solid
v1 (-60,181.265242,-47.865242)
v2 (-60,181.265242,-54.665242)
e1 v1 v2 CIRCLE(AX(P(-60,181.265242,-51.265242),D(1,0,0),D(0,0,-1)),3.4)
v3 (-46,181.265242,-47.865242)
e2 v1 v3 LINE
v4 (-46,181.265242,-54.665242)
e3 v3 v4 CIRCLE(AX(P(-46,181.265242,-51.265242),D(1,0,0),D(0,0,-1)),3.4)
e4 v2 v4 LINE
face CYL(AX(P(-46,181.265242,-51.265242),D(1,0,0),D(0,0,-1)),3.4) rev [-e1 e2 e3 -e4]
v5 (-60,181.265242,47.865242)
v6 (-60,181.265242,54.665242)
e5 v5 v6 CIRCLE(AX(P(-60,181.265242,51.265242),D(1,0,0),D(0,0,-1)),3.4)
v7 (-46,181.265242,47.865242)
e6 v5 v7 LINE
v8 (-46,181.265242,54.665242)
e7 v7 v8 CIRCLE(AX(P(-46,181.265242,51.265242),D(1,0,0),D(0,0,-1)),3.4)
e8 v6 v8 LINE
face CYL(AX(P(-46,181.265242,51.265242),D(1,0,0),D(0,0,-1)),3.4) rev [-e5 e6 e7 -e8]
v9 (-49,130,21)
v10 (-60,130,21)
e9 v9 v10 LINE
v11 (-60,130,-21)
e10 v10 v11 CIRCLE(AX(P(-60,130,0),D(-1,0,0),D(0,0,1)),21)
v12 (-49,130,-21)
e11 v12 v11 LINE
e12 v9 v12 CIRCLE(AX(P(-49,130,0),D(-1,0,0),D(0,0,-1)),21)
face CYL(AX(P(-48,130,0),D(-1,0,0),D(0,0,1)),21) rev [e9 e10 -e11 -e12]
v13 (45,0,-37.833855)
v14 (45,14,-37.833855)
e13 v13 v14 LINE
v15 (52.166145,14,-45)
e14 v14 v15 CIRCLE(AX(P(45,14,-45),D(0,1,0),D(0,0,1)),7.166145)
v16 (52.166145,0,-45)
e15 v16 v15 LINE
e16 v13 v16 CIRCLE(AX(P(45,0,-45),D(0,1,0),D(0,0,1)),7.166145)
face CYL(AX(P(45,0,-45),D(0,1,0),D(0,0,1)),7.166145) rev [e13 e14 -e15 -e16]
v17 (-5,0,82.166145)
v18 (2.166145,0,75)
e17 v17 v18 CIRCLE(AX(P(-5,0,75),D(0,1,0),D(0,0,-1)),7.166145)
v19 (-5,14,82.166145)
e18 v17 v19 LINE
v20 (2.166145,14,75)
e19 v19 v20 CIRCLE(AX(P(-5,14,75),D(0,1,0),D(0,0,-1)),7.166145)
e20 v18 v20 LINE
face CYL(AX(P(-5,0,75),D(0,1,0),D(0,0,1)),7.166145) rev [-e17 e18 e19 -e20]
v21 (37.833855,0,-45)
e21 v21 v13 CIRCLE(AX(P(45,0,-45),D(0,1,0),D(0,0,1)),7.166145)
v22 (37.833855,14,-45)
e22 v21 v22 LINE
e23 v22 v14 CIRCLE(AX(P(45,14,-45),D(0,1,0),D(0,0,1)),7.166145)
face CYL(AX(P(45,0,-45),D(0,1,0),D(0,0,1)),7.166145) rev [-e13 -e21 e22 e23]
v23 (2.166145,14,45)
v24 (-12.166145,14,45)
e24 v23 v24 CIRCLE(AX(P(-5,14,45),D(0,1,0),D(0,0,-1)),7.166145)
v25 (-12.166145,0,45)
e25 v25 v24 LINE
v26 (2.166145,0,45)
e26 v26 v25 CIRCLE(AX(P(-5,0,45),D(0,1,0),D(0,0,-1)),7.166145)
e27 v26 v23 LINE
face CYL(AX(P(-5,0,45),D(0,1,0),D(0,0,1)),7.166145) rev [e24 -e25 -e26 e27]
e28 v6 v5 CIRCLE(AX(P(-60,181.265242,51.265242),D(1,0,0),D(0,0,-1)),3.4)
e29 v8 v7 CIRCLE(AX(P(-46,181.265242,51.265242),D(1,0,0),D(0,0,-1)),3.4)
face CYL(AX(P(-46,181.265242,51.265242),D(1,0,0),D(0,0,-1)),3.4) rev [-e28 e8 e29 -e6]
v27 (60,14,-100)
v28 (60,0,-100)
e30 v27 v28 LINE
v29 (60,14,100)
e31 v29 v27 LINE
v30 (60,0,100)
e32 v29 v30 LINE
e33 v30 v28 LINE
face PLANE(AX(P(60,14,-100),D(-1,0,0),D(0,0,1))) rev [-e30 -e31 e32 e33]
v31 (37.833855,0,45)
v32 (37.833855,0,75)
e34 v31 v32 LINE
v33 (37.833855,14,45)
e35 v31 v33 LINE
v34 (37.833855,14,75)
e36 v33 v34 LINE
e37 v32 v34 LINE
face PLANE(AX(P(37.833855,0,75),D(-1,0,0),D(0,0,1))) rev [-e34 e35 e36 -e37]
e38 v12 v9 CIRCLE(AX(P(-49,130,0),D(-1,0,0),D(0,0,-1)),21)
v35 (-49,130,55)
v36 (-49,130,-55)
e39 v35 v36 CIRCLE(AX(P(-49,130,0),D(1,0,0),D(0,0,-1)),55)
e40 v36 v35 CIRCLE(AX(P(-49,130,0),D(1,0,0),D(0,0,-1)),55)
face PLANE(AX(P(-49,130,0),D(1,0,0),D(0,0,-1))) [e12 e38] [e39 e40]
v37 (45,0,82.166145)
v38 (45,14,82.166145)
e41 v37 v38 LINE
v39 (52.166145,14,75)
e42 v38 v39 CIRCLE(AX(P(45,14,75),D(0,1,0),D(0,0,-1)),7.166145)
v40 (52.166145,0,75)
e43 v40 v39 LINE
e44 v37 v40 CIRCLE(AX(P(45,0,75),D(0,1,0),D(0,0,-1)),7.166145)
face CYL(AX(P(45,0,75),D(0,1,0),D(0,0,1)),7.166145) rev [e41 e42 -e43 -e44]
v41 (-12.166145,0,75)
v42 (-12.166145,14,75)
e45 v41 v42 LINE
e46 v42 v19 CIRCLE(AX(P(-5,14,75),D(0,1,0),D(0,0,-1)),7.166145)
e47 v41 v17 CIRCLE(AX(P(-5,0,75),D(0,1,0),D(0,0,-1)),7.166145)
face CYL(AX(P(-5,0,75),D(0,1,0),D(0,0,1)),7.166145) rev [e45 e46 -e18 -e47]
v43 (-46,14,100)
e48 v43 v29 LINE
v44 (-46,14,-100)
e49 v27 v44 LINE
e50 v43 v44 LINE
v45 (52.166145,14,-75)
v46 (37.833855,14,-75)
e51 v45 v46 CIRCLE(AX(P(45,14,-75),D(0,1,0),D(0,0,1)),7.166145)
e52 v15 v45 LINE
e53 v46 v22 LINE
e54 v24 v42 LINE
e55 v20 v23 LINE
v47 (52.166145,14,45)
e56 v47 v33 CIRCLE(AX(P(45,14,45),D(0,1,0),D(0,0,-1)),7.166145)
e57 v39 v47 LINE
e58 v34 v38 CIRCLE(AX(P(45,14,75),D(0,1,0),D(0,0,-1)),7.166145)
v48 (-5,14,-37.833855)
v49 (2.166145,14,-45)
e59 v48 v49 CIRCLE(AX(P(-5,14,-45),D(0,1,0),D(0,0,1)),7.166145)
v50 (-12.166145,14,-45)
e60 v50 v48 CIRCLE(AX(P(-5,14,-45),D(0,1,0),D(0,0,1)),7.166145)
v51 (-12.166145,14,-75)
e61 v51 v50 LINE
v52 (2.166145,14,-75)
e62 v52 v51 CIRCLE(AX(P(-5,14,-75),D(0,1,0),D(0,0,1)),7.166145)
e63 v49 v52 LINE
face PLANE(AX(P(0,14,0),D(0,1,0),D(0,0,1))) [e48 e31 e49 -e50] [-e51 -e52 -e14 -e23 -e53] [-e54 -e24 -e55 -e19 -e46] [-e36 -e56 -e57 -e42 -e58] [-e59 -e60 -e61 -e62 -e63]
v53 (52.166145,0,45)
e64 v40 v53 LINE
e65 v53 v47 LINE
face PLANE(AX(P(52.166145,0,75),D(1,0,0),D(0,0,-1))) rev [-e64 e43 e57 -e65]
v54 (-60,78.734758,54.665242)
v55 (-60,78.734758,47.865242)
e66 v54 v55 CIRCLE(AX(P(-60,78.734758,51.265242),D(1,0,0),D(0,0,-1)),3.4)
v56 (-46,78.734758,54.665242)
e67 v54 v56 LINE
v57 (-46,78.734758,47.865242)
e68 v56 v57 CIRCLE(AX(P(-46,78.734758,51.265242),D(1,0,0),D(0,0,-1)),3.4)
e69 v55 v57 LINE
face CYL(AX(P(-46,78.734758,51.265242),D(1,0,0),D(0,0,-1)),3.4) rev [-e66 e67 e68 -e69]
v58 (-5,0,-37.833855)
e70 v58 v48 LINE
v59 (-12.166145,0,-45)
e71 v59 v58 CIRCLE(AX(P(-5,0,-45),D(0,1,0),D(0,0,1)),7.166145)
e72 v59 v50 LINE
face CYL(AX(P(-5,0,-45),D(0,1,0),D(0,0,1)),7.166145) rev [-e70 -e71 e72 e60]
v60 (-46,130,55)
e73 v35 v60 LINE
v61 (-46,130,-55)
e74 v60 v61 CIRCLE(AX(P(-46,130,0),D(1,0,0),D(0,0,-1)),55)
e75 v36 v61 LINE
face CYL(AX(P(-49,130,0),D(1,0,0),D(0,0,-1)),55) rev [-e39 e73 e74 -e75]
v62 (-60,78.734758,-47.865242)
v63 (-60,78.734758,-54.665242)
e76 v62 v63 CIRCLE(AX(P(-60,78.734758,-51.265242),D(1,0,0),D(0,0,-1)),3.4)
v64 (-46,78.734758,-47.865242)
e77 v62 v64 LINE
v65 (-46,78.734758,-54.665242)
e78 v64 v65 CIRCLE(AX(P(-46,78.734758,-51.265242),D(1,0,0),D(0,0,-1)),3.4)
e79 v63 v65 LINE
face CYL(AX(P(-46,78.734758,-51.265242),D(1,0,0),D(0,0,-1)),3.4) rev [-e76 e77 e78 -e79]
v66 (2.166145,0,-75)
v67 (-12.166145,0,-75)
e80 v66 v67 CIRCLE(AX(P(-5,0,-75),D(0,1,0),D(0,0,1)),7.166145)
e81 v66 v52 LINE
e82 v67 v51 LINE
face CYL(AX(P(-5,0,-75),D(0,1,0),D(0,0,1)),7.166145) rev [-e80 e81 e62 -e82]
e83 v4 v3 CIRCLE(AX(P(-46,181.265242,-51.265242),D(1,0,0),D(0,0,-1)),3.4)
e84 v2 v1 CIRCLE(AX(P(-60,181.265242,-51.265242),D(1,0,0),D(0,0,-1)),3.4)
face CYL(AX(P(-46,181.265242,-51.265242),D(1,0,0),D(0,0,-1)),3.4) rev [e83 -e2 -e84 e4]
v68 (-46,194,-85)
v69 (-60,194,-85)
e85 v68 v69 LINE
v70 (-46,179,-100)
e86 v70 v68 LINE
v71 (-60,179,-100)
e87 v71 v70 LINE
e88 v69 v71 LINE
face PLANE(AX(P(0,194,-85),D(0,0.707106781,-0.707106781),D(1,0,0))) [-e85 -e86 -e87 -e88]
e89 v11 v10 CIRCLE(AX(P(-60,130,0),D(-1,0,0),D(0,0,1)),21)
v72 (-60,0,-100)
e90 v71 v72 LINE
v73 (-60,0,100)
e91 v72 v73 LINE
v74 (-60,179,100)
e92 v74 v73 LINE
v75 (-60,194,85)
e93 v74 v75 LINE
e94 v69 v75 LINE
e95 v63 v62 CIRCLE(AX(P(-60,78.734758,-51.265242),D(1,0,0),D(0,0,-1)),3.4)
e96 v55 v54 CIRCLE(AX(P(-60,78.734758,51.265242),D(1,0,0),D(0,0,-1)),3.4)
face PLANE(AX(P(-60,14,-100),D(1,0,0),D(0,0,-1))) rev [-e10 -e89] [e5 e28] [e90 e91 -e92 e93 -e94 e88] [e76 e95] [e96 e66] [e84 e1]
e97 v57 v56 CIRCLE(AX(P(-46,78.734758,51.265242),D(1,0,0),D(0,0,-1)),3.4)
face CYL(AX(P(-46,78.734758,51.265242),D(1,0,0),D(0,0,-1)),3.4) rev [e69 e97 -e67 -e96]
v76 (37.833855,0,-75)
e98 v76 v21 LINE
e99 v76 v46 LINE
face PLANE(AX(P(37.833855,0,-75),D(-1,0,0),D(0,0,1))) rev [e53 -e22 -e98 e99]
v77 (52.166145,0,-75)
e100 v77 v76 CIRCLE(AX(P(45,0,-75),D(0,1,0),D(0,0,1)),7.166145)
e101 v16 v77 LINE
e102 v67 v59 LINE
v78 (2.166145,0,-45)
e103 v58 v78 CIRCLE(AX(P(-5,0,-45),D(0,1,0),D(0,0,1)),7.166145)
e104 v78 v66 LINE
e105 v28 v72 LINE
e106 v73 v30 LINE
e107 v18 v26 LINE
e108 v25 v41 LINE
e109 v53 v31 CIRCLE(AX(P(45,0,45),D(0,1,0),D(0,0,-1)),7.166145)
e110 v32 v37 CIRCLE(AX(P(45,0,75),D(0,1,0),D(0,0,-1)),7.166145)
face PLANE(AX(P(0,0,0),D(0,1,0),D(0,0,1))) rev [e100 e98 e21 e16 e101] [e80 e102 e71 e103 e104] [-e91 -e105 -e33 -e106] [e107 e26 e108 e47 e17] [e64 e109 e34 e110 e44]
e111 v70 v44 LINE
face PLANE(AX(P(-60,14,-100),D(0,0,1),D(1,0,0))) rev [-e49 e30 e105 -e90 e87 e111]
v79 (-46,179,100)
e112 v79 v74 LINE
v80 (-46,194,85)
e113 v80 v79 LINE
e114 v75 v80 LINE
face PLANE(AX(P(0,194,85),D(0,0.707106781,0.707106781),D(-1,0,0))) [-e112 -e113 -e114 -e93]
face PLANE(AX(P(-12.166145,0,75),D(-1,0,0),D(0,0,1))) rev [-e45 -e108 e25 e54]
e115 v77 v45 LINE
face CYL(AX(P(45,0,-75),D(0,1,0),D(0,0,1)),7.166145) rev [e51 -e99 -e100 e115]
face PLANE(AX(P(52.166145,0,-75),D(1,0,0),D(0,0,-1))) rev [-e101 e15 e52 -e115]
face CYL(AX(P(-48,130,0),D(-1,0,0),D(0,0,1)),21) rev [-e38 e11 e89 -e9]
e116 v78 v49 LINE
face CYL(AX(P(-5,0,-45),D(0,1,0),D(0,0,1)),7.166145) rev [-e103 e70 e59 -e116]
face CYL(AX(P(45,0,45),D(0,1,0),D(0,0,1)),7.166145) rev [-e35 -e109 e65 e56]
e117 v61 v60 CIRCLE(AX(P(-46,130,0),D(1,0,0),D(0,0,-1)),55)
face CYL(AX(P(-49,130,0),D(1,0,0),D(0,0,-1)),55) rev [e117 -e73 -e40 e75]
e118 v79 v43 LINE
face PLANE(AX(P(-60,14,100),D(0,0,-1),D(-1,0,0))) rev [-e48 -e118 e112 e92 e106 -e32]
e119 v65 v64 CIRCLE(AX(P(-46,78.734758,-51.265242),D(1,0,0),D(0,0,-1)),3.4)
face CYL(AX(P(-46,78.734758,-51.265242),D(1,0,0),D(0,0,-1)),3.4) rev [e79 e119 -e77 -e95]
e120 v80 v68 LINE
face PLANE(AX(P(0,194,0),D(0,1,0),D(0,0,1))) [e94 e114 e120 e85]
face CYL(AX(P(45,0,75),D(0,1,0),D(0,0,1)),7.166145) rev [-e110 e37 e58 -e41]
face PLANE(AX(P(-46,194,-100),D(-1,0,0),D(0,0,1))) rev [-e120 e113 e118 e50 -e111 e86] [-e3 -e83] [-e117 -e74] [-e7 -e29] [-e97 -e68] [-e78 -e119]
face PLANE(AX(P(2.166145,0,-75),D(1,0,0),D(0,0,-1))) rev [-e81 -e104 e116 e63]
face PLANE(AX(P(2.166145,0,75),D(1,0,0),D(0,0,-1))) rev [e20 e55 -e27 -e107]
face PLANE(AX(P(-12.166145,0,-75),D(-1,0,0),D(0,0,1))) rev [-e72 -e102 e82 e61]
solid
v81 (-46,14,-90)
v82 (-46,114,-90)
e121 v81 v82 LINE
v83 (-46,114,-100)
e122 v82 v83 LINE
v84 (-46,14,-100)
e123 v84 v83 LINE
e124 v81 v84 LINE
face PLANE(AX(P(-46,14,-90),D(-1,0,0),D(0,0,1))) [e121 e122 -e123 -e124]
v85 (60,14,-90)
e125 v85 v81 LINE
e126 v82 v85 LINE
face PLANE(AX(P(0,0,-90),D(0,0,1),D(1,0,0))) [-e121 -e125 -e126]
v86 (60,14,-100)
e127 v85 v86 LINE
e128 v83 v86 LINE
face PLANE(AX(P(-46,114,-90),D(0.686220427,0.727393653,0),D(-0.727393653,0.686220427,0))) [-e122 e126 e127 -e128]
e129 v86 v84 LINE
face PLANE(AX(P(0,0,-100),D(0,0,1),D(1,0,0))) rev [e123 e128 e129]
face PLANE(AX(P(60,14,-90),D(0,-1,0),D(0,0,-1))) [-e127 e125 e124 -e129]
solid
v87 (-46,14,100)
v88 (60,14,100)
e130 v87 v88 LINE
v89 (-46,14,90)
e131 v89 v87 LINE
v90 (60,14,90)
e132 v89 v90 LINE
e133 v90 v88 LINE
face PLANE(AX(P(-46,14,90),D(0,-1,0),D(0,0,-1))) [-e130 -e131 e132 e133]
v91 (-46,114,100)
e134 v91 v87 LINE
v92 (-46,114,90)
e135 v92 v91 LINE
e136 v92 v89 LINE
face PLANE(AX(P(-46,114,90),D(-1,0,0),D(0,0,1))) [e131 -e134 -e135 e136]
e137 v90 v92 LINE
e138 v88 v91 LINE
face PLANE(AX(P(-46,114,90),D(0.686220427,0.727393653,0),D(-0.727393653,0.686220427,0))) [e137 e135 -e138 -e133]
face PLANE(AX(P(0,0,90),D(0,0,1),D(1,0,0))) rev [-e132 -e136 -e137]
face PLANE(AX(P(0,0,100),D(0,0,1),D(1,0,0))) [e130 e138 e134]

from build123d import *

# Parameters (mm, degrees)
SKETCH_1_W               = 120
SKETCH_1_H               = 200
EXTRUDE_1_DEPTH          = 14
SKETCH_2_W               = 14
SKETCH_2_H               = 200
EXTRUDE_2_DEPTH          = 180
EXTRUDE_3_DEPTH          = 10
EXTRUDE_4_DEPTH          = 10
SKETCH_5_R               = 21
CUT_EXTRUDE_1_DEPTH      = 12
SKETCH_6_R               = 15
CUT_EXTRUDE_2_DEPTH      = 244.515913238
SKETCH_7_R               = 55
CUT_EXTRUDE_3_DEPTH      = 3
CUT_EXTRUDE_4_DEPTH      = 215.476105895
SKETCH_10_W              = 3.4
SKETCH_10_H              = 14
PATTERN_CIRCULAR_1_COUNT = 4
CHAMFER_1_SIZE           = 15


with BuildPart() as part:
    # 草图1 → 凸台-拉伸1 (new body)
    with BuildSketch(Plane(origin=(0, 0, 0), x_dir=(1, 0, 0), z_dir=(0, 1, 0))):
        Rectangle(SKETCH_1_W, SKETCH_1_H)
    extrude(amount=EXTRUDE_1_DEPTH)

    # 草图2 → 凸台-拉伸2 (add)
    with BuildSketch(Plane(origin=(0, 14, 0), x_dir=(1, 0, 0), z_dir=(0, 1, 0))):
        with Locations((-53, 0)):
            Rectangle(SKETCH_2_W, SKETCH_2_H)
    extrude(amount=EXTRUDE_2_DEPTH)

    # 草图5 → 切除-拉伸1 (cut)
    with BuildSketch(Plane.ZY.offset(60)):
        with Locations((0, 130)):
            Circle(SKETCH_5_R)
    extrude(amount=-CUT_EXTRUDE_1_DEPTH, mode=Mode.SUBTRACT)

    # 草图6 → 切除-拉伸2 (cut, through all)
    with BuildSketch(Plane.ZY.offset(48)):
        with Locations((0, 130)):
            Circle(SKETCH_6_R)
    extrude(amount=-CUT_EXTRUDE_2_DEPTH, mode=Mode.SUBTRACT)

    # 草图7 → 切除-拉伸3 (cut)
    with BuildSketch(Plane(origin=(-46, 0, 0), x_dir=(0, 0, -1), z_dir=(1, 0, 0))):
        with Locations((0, 130)):
            Circle(SKETCH_7_R)
    extrude(amount=-CUT_EXTRUDE_3_DEPTH, mode=Mode.SUBTRACT)

    # 草图8 → 切除-拉伸4 (cut, through all)
    with BuildSketch(Plane(origin=(0, 14, 0), x_dir=(1, 0, 0), z_dir=(0, 1, 0))):
        with BuildLine():
            Line((2.166144886, 75), (2.166144886, 45))
            ThreePointArc((2.166144886, 45), (-5, 37.833855114), (-12.166144886, 45))
            Line((-12.166144886, 45), (-12.166144886, 75))
            ThreePointArc((-12.166144886, 75), (-5, 82.166144886), (2.166144886, 75))
        make_face()
        with BuildLine():
            Line((52.166144886, 75), (52.166144886, 45))
            ThreePointArc((52.166144886, 45), (45, 37.833855114), (37.833855114, 45))
            Line((37.833855114, 45), (37.833855114, 75))
            ThreePointArc((37.833855114, 75), (45, 82.166144886), (52.166144886, 75))
        make_face()
        with BuildLine():
            Line((2.166144886, -75), (2.166144886, -45))
            ThreePointArc((2.166144886, -45), (-5, -37.833855114), (-12.166144886, -45))
            Line((-12.166144886, -45), (-12.166144886, -75))
            ThreePointArc((-12.166144886, -75), (-5, -82.166144886), (2.166144886, -75))
        make_face()
        with BuildLine():
            Line((52.166144886, -75), (52.166144886, -45))
            ThreePointArc((52.166144886, -45), (45, -37.833855114), (37.833855114, -45))
            Line((37.833855114, -45), (37.833855114, -75))
            ThreePointArc((37.833855114, -75), (45, -82.166144886), (52.166144886, -75))
        make_face()
    extrude(amount=-CUT_EXTRUDE_4_DEPTH, mode=Mode.SUBTRACT)

    # 草图10 → M8 螺纹孔1 (revolve, cut)
    with BuildSketch(Plane(origin=(-46, 181.265241636, 51.265241636), x_dir=(0, 0, -1), z_dir=(0, 1, 0))):
        with Locations((1.7, 7)):
            Rectangle(SKETCH_10_W, SKETCH_10_H)
    hole_wizard_m8_1 = revolve(axis=Axis((-39.65, 181.265241636, 51.265241636), (-1, 0, 0)), mode=Mode.SUBTRACT)

    # 阵列(圆周)1: M8 螺纹孔1 ×4 about axis
    pattern_circular_1_axis = Axis((0, 130, 0), (1, 0, 0))
    for i in range(1, PATTERN_CIRCULAR_1_COUNT):
        add(hole_wizard_m8_1.rotate(pattern_circular_1_axis, i * 360 / PATTERN_CIRCULAR_1_COUNT), mode=Mode.SUBTRACT)

    # 倒角1
    chamfer_1_edges = [part.edges().sort_by_distance(p)[0] for p in [
        (-53, 194, 100),
        (-53, 194, -100),
    ]]
    chamfer(chamfer_1_edges, length=CHAMFER_1_SIZE)


with BuildPart() as body_2:
    # 草图3 → 凸台-拉伸3 (new body)
    with BuildSketch(Plane.XY.offset(100)):
        Polygon((-46, 114), (60, 14), (-46, 14), align=None)
    extrude(amount=-EXTRUDE_3_DEPTH)


with BuildPart() as body_3:
    # 草图4 → 凸台-拉伸4 (new body)
    with BuildSketch(Plane(origin=(0, 0, -100), x_dir=(-1, 0, 0), z_dir=(0, 0, -1))):
        Polygon((46, 14), (46, 114), (-60, 14), align=None)
    extrude(amount=-EXTRUDE_4_DEPTH)


solid = Compound([part.part, body_2.part, body_3.part])
